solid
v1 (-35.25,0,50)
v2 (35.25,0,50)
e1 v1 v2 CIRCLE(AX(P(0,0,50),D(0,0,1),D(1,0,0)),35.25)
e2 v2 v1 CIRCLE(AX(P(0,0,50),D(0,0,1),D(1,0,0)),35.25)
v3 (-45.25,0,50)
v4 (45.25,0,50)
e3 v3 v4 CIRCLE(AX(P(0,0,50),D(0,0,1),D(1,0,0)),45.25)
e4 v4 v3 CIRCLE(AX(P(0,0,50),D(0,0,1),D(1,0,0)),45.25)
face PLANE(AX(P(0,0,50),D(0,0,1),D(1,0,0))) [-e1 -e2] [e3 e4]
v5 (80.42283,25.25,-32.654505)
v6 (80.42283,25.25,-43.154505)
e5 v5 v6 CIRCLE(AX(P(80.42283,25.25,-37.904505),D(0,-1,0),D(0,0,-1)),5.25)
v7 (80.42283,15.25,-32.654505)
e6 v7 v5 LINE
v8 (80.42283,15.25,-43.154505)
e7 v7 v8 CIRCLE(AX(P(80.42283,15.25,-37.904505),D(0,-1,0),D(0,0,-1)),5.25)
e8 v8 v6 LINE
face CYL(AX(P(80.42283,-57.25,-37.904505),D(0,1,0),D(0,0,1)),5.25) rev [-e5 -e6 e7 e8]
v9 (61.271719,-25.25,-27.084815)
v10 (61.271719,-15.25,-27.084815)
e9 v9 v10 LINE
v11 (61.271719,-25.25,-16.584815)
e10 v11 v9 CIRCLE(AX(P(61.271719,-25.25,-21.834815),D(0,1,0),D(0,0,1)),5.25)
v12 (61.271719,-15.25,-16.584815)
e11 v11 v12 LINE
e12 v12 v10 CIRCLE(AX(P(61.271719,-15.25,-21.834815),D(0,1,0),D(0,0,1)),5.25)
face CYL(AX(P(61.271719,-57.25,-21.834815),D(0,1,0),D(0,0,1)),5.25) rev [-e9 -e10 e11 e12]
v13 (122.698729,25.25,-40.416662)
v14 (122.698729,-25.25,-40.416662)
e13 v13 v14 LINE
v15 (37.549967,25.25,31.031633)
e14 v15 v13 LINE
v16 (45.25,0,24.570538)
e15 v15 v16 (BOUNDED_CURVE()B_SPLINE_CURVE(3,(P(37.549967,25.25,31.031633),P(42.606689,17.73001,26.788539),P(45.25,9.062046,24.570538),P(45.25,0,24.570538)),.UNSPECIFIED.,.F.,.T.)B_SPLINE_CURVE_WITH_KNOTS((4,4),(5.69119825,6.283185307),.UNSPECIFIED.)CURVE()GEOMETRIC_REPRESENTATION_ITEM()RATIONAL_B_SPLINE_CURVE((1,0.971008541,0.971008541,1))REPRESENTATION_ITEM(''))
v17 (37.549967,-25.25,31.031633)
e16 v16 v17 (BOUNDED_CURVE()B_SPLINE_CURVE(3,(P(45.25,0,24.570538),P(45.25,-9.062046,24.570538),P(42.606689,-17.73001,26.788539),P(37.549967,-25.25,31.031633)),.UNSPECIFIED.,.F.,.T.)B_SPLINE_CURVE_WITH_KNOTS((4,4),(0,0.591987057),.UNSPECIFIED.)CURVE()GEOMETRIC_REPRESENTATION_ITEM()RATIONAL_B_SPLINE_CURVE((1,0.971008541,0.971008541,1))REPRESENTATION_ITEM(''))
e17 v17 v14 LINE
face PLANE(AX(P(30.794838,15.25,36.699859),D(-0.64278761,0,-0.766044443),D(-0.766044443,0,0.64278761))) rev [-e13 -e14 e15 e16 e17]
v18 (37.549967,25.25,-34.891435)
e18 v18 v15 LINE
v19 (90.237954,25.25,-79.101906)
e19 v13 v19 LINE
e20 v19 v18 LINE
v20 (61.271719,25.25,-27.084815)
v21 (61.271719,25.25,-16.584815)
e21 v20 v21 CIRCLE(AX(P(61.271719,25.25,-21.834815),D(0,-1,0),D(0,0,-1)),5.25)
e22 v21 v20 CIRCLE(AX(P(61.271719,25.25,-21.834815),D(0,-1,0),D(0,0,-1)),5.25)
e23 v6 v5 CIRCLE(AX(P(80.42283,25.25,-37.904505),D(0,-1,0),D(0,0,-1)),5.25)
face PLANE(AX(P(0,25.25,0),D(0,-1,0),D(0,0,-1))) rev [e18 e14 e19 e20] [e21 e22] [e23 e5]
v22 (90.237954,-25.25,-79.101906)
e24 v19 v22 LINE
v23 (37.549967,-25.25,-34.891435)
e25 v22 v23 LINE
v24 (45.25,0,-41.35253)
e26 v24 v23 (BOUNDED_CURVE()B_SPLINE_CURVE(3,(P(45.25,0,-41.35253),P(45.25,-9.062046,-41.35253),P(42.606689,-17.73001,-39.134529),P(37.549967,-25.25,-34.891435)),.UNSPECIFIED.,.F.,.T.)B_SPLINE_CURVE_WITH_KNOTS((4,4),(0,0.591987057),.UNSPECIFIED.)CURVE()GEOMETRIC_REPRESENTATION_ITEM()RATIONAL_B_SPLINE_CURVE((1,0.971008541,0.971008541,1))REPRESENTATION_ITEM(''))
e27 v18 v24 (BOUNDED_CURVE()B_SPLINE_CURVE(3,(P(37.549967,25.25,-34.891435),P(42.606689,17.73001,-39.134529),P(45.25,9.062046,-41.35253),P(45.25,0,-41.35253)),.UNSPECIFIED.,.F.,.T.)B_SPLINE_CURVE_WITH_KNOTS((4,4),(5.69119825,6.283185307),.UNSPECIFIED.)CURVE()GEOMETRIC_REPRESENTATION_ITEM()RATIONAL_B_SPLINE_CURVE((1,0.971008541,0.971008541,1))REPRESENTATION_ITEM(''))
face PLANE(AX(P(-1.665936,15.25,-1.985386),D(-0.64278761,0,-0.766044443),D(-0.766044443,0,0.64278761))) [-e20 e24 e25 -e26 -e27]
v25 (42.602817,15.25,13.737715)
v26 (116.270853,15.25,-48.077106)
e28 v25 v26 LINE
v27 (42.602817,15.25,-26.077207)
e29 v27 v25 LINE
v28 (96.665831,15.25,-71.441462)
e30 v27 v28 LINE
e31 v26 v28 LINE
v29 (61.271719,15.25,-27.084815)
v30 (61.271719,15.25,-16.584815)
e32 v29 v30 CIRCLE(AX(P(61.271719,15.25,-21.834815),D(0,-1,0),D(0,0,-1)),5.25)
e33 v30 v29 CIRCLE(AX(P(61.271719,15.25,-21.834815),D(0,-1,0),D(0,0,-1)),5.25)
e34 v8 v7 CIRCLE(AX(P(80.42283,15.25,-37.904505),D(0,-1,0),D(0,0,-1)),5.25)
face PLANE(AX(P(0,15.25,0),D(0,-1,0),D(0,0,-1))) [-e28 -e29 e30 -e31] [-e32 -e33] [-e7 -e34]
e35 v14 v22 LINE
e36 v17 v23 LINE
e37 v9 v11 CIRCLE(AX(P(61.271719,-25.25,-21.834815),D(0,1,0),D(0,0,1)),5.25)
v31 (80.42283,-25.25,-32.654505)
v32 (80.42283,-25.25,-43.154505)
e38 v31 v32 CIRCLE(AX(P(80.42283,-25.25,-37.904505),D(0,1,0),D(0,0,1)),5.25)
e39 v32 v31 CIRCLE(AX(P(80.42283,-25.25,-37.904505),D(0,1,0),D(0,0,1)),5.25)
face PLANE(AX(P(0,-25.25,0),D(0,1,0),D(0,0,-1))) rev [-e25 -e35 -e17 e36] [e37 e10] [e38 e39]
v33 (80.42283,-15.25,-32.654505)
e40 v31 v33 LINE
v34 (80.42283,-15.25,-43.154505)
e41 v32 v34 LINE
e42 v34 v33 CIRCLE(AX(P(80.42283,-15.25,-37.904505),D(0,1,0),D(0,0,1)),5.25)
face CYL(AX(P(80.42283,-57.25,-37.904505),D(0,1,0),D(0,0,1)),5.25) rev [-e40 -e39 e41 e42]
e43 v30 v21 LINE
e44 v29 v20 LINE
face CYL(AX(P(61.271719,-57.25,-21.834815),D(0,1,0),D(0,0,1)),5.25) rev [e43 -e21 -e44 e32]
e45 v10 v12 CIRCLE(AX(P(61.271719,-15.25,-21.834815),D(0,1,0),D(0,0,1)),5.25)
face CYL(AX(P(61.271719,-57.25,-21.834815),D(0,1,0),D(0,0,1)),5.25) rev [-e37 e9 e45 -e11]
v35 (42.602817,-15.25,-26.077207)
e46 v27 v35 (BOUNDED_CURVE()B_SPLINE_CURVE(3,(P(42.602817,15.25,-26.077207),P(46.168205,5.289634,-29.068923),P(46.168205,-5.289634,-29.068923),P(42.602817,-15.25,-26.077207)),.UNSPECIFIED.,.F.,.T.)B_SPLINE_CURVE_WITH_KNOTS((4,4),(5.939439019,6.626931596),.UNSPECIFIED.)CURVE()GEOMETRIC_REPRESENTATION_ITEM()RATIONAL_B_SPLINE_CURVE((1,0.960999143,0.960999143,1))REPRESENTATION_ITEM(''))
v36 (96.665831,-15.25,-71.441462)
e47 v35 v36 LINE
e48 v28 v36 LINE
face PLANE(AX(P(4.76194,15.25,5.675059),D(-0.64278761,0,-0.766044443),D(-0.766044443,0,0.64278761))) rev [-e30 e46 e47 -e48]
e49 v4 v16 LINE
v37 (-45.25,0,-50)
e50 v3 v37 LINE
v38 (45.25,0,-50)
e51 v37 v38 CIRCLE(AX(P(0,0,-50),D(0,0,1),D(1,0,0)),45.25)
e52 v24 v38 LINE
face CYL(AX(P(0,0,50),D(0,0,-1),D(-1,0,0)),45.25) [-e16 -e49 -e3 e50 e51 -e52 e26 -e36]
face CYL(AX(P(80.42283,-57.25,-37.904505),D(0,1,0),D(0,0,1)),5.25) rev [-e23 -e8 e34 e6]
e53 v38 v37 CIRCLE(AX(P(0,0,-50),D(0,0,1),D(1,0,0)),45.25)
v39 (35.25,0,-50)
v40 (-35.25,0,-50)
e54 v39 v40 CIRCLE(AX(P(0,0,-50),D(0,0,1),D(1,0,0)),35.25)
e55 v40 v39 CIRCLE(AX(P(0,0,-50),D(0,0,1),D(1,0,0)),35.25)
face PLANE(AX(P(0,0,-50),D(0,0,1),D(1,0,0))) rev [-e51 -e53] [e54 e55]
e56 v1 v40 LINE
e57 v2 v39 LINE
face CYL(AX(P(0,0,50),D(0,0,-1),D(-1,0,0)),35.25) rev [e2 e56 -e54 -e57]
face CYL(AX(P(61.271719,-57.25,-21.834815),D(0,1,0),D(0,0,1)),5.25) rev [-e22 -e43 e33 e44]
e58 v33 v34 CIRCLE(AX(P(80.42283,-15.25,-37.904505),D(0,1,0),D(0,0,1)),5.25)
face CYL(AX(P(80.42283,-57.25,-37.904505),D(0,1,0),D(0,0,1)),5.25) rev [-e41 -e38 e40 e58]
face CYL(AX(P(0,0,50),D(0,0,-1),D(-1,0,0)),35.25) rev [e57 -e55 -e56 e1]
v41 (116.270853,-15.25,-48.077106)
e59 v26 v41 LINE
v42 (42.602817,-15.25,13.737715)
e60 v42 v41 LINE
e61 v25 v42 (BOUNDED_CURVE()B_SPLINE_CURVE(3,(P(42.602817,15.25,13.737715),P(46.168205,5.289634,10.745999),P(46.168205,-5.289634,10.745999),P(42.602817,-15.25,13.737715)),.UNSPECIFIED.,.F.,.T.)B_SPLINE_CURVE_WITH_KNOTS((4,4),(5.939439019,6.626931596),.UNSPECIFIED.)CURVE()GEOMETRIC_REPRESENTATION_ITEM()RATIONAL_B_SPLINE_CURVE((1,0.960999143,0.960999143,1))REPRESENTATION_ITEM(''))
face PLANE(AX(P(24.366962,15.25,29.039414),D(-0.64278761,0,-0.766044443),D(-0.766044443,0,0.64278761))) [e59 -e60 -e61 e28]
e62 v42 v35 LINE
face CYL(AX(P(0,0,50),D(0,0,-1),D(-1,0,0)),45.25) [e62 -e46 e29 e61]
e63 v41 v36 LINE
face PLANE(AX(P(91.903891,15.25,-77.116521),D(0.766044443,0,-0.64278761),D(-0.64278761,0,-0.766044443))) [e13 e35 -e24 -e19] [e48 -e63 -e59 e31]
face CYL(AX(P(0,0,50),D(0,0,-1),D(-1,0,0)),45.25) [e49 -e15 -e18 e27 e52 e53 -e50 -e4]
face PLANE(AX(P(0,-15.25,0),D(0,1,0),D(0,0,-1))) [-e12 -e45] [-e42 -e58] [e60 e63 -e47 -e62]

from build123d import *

# Parameters (mm, degrees)
SKETCH_1_R          = 45.25
SKETCH_1_R_2        = 35.25
EXTRUDE_1_DEPTH     = 50
EXTRUDE_2_DEPTH     = 15.25
EXTRUDE_3_DEPTH     = 10
SKETCH_5_R          = 5.25
CUT_EXTRUDE_1_DEPTH = 82.5


with BuildPart() as part:
    # 草图1 → 凸台-拉伸1 (new, symmetric)
    with BuildSketch(Plane.XY):
        Circle(SKETCH_1_R)
        Circle(SKETCH_1_R_2, mode=Mode.SUBTRACT)
    extrude(amount=EXTRUDE_1_DEPTH, both=True)

    # 草图2 → 凸台-拉伸2 (add, symmetric)
    with BuildSketch(Plane(origin=(0, 0, 0), x_dir=(1, 0, 0), z_dir=(0, 1, 0))):
        Polygon((90.237954411, 79.101906321), (35.25, 32.961534056), (35.25, 19.907461162), (96.665830508, 71.44146189), align=None)
        Polygon((122.6987287, 40.416661944), (116.270852604, 48.077106375), (35.25, -19.907461162), (35.25, -32.961534056), align=None)
    extrude(amount=EXTRUDE_2_DEPTH, both=True)

    # 草图4 → 凸台-拉伸3 (add)
    with BuildSketch(Plane(origin=(0, 15.25, 0), x_dir=(1, 0, 0), z_dir=(0, 1, 0))):
        Polygon((90.237954411, 79.101906321), (122.6987287, 40.416661944), (35.25, -32.961534056), (35.25, 32.961534056), align=None)
    extrude_3 = extrude(amount=EXTRUDE_3_DEPTH)

    # 镜向1: 凸台-拉伸3 across plane
    add(extrude_3.mirror(Plane.ZX))

    # 草图5 → 切除-拉伸1 (cut, symmetric)
    with BuildSketch(Plane(origin=(0, 25.25, 0), x_dir=(1, 0, 0), z_dir=(0, 1, 0))):
        with Locations(Location((80.42283049, 37.904505403, 0), (0, 0, 270))):
            Circle(SKETCH_5_R)
        with Locations(Location((61.271719412, 21.834815161, 0), (0, 0, 270))):
            Circle(SKETCH_5_R)
    extrude(amount=CUT_EXTRUDE_1_DEPTH, both=True, mode=Mode.SUBTRACT)


solid = part.part
